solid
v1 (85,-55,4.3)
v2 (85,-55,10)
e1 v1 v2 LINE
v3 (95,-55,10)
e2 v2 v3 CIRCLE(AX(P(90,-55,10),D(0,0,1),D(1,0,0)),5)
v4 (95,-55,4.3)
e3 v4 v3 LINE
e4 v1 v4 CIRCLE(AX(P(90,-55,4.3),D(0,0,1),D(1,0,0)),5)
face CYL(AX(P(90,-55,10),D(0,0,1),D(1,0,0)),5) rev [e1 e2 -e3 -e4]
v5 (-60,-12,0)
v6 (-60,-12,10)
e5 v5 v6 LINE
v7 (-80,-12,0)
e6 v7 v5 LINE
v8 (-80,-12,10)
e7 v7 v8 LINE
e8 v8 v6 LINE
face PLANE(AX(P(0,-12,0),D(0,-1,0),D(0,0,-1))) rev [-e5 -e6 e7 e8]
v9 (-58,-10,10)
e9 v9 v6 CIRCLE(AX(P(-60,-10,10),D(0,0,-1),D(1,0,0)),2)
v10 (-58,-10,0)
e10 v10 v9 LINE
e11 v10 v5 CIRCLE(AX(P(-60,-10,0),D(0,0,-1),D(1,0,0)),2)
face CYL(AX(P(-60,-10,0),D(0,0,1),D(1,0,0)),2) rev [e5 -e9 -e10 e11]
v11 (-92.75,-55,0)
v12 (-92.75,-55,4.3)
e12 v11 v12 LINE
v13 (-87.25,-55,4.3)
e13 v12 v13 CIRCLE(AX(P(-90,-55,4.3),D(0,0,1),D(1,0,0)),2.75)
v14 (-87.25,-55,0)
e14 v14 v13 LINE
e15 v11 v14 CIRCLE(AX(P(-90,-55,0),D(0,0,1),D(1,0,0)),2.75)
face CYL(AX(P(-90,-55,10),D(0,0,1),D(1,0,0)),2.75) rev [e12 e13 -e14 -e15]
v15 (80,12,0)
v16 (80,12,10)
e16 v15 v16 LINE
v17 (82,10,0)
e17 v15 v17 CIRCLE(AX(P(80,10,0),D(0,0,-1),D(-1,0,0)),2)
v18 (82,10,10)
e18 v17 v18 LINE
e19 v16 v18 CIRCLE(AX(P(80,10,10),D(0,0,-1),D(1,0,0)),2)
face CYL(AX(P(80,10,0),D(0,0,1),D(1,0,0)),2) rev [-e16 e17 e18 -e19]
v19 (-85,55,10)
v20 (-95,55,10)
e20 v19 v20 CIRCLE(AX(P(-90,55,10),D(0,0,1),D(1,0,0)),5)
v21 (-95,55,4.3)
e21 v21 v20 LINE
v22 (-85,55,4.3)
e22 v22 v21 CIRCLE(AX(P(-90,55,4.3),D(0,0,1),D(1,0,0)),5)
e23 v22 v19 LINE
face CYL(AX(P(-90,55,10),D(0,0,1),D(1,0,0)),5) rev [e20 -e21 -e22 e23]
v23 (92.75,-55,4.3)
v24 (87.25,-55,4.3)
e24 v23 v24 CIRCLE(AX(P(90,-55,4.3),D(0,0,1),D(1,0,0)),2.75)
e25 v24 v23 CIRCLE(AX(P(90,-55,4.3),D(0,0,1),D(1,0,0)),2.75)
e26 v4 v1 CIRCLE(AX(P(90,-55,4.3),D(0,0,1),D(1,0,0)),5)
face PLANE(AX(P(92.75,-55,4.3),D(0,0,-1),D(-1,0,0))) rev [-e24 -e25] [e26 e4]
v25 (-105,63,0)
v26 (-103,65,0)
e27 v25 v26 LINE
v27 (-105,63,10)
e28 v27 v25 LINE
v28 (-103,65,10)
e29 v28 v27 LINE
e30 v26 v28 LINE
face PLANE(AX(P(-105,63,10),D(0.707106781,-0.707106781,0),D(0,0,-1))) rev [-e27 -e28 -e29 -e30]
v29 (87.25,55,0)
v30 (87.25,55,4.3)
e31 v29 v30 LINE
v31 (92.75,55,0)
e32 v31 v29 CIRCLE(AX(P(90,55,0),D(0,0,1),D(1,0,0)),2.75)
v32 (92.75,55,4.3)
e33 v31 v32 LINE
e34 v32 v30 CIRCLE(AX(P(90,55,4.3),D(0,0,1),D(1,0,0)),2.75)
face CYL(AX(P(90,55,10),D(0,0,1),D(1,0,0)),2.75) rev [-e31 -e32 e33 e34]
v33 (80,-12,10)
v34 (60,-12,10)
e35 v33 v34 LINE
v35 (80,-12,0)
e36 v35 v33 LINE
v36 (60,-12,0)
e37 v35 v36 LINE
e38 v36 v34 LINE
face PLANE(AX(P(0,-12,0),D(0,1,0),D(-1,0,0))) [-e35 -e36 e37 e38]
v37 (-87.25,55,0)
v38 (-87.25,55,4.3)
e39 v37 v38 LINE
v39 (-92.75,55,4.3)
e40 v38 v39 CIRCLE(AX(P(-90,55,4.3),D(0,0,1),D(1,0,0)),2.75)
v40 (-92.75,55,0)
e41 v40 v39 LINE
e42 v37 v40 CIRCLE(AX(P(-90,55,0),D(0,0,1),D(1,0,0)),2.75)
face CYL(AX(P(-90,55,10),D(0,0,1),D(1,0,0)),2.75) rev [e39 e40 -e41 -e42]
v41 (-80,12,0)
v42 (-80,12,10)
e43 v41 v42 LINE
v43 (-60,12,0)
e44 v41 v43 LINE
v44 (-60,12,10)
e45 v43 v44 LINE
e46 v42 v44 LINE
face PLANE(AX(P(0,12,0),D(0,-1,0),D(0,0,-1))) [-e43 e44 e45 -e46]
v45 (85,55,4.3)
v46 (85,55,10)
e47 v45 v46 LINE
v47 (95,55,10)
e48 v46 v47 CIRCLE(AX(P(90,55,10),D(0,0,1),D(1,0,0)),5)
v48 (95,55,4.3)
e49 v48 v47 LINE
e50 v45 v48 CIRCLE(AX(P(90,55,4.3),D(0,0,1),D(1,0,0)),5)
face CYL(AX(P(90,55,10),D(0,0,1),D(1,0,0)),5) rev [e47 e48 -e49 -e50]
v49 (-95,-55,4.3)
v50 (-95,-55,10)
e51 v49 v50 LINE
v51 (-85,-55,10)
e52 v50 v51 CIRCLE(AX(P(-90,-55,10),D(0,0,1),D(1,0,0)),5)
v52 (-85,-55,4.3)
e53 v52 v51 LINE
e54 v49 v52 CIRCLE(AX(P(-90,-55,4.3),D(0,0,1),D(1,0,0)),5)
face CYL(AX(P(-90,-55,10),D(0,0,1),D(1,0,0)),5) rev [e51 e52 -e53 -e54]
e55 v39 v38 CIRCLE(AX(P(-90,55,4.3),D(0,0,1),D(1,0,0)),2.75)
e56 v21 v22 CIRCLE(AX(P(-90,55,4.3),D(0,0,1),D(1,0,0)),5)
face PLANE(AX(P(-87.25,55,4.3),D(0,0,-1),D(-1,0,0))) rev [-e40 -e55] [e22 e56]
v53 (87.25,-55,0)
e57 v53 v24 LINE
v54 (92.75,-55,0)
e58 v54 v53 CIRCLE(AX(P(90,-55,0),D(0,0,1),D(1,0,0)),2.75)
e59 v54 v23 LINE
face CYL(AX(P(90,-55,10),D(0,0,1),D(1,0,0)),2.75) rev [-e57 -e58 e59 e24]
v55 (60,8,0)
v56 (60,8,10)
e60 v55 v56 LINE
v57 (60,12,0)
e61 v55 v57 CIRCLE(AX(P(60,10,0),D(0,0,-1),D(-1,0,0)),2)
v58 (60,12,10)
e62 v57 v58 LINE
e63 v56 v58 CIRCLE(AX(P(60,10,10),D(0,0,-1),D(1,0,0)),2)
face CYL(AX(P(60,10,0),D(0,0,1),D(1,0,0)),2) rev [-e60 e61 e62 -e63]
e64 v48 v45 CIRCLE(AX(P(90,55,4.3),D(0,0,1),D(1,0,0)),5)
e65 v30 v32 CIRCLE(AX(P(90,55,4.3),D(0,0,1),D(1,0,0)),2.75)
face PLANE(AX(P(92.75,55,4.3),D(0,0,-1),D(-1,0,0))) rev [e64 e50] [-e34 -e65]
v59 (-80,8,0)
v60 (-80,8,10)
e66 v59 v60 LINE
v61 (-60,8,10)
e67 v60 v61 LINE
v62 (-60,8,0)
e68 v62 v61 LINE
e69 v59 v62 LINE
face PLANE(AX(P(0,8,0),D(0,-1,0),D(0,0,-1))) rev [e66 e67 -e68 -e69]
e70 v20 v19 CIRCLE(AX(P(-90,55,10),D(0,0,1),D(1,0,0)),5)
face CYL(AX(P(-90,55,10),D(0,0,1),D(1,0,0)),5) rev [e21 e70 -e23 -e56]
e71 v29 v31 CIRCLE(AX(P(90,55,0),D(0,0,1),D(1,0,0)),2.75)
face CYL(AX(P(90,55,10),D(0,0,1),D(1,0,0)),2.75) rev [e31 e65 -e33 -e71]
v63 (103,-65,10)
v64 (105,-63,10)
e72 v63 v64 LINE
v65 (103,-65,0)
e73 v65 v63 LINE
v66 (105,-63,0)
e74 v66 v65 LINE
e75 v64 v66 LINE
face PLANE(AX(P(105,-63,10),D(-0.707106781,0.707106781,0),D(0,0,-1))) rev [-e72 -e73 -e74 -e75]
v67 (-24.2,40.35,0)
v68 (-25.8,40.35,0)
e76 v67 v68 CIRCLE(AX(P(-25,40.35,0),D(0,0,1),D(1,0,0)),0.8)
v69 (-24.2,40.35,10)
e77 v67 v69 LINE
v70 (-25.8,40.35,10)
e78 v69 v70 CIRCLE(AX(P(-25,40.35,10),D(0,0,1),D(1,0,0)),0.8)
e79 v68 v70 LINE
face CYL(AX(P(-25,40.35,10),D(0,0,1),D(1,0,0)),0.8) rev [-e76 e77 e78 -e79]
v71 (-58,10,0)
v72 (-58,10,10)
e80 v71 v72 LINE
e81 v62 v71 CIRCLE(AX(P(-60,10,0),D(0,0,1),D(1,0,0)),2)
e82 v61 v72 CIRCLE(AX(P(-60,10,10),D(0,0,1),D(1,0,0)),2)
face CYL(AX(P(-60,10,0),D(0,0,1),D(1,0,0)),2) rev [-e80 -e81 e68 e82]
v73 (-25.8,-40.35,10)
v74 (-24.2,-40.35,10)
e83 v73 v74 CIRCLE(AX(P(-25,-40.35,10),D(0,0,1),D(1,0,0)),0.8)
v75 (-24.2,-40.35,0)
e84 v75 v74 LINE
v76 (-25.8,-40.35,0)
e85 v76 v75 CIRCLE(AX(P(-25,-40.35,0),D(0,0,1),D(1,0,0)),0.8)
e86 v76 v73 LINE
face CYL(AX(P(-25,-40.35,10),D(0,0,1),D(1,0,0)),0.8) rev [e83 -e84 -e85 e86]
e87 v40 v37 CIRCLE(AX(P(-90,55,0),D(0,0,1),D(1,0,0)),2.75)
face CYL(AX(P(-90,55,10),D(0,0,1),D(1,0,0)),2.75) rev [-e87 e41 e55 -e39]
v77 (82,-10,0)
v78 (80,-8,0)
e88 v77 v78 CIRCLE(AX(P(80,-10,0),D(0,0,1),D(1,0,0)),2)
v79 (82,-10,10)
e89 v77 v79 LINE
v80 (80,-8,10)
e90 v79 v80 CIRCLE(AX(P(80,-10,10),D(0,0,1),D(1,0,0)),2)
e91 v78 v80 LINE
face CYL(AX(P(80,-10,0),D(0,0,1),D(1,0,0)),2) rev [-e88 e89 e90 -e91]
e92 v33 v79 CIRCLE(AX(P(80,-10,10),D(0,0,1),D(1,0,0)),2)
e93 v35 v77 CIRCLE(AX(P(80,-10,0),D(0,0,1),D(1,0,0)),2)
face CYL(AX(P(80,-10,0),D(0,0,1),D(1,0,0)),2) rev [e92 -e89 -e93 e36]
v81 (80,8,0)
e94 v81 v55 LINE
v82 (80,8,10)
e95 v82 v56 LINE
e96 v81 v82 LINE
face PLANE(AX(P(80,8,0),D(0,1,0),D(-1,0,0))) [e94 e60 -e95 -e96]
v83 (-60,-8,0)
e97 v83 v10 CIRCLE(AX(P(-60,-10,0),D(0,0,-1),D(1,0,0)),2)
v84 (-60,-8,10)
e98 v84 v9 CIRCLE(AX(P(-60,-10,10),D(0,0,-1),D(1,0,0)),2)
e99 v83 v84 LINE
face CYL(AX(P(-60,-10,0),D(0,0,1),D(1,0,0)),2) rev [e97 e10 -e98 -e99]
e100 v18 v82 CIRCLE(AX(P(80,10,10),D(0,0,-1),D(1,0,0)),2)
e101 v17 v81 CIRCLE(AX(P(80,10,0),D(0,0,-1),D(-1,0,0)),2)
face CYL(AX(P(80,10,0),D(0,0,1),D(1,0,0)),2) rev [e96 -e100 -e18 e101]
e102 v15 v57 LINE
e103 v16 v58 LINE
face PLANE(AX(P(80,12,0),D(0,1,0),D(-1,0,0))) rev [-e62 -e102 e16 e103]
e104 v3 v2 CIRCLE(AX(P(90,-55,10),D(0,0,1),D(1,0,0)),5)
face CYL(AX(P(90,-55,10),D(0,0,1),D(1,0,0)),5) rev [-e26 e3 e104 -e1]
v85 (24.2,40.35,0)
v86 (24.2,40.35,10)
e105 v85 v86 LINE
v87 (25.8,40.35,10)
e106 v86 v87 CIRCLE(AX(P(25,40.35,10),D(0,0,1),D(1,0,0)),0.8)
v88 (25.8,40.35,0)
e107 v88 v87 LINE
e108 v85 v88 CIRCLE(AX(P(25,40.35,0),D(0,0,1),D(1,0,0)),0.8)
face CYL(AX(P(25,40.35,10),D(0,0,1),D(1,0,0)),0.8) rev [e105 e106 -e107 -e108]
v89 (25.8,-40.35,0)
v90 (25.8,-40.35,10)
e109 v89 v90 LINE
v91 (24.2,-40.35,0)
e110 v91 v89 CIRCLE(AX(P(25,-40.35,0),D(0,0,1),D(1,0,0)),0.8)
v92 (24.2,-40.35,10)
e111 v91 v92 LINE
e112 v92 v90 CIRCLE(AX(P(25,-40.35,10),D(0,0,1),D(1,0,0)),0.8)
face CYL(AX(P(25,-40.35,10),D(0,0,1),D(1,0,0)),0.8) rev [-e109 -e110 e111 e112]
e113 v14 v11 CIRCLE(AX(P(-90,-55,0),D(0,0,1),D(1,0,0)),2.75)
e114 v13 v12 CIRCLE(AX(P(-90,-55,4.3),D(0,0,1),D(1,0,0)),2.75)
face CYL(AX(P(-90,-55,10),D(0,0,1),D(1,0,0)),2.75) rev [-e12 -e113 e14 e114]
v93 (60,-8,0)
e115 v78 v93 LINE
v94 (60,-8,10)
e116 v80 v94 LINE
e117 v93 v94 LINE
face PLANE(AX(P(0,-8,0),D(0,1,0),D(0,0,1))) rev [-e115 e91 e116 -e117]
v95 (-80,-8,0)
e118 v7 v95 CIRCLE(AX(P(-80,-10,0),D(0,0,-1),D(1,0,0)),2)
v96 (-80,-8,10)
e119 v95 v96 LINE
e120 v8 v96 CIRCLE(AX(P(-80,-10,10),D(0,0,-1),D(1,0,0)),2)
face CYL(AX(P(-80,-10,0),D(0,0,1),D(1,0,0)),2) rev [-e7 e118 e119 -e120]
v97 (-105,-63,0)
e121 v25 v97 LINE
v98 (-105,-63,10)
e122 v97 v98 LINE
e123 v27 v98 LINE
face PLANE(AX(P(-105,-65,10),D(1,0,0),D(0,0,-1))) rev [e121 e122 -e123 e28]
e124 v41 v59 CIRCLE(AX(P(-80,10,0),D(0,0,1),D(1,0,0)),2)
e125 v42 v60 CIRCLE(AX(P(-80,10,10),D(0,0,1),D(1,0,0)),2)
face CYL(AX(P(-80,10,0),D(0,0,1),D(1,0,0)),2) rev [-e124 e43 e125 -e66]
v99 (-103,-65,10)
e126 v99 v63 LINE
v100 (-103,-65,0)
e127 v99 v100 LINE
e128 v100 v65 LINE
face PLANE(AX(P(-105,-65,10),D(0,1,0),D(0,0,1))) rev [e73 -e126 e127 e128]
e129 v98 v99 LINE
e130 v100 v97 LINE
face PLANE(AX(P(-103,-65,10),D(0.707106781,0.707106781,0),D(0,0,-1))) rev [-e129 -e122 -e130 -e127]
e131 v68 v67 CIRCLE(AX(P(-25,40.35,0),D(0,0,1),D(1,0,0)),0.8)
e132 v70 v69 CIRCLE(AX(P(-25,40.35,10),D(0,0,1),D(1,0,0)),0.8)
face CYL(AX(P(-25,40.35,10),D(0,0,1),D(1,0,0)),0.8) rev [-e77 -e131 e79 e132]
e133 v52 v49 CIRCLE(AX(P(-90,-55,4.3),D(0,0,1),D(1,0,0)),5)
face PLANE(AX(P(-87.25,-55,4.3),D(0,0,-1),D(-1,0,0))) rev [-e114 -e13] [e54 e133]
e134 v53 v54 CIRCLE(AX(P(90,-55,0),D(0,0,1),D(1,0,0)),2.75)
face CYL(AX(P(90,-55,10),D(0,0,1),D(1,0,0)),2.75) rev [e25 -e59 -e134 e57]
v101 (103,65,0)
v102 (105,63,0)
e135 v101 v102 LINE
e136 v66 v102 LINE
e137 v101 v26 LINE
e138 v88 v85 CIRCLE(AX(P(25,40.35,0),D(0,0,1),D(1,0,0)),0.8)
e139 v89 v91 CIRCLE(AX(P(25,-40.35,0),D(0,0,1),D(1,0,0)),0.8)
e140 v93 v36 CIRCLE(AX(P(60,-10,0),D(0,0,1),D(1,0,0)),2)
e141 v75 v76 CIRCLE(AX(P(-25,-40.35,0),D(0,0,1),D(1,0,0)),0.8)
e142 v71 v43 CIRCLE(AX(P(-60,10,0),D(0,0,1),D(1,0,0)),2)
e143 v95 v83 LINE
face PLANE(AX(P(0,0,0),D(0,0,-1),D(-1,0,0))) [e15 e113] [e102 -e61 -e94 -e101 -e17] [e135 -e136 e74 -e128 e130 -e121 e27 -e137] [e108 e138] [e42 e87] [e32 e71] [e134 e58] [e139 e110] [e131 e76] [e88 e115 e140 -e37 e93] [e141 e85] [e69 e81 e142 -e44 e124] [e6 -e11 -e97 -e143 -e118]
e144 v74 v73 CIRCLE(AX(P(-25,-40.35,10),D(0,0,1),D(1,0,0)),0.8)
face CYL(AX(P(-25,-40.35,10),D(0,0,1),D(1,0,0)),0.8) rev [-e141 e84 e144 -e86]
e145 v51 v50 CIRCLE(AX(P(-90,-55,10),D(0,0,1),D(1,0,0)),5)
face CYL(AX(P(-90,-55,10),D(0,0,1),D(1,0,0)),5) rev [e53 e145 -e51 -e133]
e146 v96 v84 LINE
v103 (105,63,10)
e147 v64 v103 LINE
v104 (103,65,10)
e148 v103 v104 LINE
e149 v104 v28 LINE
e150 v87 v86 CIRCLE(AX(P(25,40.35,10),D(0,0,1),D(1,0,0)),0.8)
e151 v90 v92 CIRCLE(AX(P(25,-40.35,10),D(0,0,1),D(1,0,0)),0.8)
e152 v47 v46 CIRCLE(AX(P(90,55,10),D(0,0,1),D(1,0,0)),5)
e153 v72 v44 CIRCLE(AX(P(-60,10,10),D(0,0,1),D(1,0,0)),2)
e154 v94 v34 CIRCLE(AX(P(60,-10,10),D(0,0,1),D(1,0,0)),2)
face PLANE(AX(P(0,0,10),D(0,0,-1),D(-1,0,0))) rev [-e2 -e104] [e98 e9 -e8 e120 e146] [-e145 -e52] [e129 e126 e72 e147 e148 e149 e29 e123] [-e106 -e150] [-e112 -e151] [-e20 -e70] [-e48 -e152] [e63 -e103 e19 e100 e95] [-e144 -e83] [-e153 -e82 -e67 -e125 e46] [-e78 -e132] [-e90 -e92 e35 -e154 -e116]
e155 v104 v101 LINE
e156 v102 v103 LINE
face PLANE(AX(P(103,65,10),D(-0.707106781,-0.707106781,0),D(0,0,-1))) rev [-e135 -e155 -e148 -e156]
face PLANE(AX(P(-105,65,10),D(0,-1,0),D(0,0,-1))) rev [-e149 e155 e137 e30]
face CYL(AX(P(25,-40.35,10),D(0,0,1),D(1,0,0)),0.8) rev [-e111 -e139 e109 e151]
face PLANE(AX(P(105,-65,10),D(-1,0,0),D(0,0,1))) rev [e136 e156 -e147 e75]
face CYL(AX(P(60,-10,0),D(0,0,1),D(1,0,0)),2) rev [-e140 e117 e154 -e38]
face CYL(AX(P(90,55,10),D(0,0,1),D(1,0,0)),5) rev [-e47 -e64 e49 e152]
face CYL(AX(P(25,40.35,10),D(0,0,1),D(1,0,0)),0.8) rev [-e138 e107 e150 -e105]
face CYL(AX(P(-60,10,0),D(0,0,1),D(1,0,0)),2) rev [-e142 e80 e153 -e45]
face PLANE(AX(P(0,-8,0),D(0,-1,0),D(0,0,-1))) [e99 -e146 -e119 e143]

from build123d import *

# Parameters (mm, degrees)
SKETCH1_W                                           = 210
SKETCH1_H                                           = 130
BOSS_EXTRUDE1_DEPTH                                 = 10
CUT_EXTRUDE1_DEPTH                                  = 124.895116934
CUT_EXTRUDE1_DEPTH_BACK                             = 124.895116934
HOLE_SIZE_PER_SOCKET_HEAD_CAP_SCREW_TYP_D           = 5.5
HOLE_SIZE_PER_SOCKET_HEAD_CAP_SCREW_TYP_CBORE_D     = 10
HOLE_SIZE_PER_SOCKET_HEAD_CAP_SCREW_TYP_CBORE_DEPTH = 5.7
M2_TAPPED_HOLE1_D                                   = 1.6
CHAMFER1_SIZE                                       = 2


with BuildPart() as part:
    # Sketch1 → Boss-Extrude1 (new body)
    with BuildSketch(Plane.XY):
        Rectangle(SKETCH1_W, SKETCH1_H)
    extrude(amount=BOSS_EXTRUDE1_DEPTH)

    # Sketch2 → Cut-Extrude1 (cut, two sides: drawn at the far end of the back side and taken through both)
    with BuildSketch(Plane.XY.offset(10).offset(-CUT_EXTRUDE1_DEPTH_BACK)):
        with BuildLine():
            Line((-80, 8), (-60, 8))
            ThreePointArc((-60, 8), (-58, 10), (-60, 12))
            Line((-60, 12), (-80, 12))
            ThreePointArc((-80, 12), (-82, 10), (-80, 8))
        make_face()
        with BuildLine():
            ThreePointArc((-60, -8), (-58, -10), (-60, -12))
            Line((-60, -12), (-80, -12))
            ThreePointArc((-80, -12), (-82, -10), (-80, -8))
            Line((-80, -8), (-60, -8))
        make_face()
        with BuildLine():
            Line((80, -8), (60, -8))
            ThreePointArc((60, -8), (58, -10), (60, -12))
            Line((60, -12), (80, -12))
            ThreePointArc((80, -12), (82, -10), (80, -8))
        make_face()
        with BuildLine():
            Line((80, 12), (60, 12))
            ThreePointArc((60, 12), (58, 10), (60, 8))
            Line((60, 8), (80, 8))
            ThreePointArc((80, 8), (82, 10), (80, 12))
        make_face()
    extrude(amount=CUT_EXTRUDE1_DEPTH + CUT_EXTRUDE1_DEPTH_BACK, mode=Mode.SUBTRACT)

    # Hole size (per socket head cap screw type)1 (through all)
    with Locations(Plane(origin=(-90, 55, 10), x_dir=(1, 0, 0), z_dir=(0, 0, 1))):
        with Locations((0, 0), (0, -110), (180, -110), (180, 0)):
            CounterBoreHole(HOLE_SIZE_PER_SOCKET_HEAD_CAP_SCREW_TYP_D / 2, HOLE_SIZE_PER_SOCKET_HEAD_CAP_SCREW_TYP_CBORE_D / 2, HOLE_SIZE_PER_SOCKET_HEAD_CAP_SCREW_TYP_CBORE_DEPTH)

    # M2 Tapped Hole1 (through all)
    with Locations(Plane(origin=(-25, 40.35, 10), x_dir=(1, 0, 0), z_dir=(0, 0, 1))):
        with Locations((0, 0), (50, 0), (50, -80.7), (0, -80.7)):
            Hole(M2_TAPPED_HOLE1_D / 2)

    # Chamfer1
    chamfer1_edges = [part.edges().sort_by_distance(p)[0] for p in [
        (105, -65, 5),
        (-105, -65, 5),
        (-105, 65, 5),
        (105, 65, 5),
    ]]
    chamfer(chamfer1_edges, length=CHAMFER1_SIZE)


solid = part.part
